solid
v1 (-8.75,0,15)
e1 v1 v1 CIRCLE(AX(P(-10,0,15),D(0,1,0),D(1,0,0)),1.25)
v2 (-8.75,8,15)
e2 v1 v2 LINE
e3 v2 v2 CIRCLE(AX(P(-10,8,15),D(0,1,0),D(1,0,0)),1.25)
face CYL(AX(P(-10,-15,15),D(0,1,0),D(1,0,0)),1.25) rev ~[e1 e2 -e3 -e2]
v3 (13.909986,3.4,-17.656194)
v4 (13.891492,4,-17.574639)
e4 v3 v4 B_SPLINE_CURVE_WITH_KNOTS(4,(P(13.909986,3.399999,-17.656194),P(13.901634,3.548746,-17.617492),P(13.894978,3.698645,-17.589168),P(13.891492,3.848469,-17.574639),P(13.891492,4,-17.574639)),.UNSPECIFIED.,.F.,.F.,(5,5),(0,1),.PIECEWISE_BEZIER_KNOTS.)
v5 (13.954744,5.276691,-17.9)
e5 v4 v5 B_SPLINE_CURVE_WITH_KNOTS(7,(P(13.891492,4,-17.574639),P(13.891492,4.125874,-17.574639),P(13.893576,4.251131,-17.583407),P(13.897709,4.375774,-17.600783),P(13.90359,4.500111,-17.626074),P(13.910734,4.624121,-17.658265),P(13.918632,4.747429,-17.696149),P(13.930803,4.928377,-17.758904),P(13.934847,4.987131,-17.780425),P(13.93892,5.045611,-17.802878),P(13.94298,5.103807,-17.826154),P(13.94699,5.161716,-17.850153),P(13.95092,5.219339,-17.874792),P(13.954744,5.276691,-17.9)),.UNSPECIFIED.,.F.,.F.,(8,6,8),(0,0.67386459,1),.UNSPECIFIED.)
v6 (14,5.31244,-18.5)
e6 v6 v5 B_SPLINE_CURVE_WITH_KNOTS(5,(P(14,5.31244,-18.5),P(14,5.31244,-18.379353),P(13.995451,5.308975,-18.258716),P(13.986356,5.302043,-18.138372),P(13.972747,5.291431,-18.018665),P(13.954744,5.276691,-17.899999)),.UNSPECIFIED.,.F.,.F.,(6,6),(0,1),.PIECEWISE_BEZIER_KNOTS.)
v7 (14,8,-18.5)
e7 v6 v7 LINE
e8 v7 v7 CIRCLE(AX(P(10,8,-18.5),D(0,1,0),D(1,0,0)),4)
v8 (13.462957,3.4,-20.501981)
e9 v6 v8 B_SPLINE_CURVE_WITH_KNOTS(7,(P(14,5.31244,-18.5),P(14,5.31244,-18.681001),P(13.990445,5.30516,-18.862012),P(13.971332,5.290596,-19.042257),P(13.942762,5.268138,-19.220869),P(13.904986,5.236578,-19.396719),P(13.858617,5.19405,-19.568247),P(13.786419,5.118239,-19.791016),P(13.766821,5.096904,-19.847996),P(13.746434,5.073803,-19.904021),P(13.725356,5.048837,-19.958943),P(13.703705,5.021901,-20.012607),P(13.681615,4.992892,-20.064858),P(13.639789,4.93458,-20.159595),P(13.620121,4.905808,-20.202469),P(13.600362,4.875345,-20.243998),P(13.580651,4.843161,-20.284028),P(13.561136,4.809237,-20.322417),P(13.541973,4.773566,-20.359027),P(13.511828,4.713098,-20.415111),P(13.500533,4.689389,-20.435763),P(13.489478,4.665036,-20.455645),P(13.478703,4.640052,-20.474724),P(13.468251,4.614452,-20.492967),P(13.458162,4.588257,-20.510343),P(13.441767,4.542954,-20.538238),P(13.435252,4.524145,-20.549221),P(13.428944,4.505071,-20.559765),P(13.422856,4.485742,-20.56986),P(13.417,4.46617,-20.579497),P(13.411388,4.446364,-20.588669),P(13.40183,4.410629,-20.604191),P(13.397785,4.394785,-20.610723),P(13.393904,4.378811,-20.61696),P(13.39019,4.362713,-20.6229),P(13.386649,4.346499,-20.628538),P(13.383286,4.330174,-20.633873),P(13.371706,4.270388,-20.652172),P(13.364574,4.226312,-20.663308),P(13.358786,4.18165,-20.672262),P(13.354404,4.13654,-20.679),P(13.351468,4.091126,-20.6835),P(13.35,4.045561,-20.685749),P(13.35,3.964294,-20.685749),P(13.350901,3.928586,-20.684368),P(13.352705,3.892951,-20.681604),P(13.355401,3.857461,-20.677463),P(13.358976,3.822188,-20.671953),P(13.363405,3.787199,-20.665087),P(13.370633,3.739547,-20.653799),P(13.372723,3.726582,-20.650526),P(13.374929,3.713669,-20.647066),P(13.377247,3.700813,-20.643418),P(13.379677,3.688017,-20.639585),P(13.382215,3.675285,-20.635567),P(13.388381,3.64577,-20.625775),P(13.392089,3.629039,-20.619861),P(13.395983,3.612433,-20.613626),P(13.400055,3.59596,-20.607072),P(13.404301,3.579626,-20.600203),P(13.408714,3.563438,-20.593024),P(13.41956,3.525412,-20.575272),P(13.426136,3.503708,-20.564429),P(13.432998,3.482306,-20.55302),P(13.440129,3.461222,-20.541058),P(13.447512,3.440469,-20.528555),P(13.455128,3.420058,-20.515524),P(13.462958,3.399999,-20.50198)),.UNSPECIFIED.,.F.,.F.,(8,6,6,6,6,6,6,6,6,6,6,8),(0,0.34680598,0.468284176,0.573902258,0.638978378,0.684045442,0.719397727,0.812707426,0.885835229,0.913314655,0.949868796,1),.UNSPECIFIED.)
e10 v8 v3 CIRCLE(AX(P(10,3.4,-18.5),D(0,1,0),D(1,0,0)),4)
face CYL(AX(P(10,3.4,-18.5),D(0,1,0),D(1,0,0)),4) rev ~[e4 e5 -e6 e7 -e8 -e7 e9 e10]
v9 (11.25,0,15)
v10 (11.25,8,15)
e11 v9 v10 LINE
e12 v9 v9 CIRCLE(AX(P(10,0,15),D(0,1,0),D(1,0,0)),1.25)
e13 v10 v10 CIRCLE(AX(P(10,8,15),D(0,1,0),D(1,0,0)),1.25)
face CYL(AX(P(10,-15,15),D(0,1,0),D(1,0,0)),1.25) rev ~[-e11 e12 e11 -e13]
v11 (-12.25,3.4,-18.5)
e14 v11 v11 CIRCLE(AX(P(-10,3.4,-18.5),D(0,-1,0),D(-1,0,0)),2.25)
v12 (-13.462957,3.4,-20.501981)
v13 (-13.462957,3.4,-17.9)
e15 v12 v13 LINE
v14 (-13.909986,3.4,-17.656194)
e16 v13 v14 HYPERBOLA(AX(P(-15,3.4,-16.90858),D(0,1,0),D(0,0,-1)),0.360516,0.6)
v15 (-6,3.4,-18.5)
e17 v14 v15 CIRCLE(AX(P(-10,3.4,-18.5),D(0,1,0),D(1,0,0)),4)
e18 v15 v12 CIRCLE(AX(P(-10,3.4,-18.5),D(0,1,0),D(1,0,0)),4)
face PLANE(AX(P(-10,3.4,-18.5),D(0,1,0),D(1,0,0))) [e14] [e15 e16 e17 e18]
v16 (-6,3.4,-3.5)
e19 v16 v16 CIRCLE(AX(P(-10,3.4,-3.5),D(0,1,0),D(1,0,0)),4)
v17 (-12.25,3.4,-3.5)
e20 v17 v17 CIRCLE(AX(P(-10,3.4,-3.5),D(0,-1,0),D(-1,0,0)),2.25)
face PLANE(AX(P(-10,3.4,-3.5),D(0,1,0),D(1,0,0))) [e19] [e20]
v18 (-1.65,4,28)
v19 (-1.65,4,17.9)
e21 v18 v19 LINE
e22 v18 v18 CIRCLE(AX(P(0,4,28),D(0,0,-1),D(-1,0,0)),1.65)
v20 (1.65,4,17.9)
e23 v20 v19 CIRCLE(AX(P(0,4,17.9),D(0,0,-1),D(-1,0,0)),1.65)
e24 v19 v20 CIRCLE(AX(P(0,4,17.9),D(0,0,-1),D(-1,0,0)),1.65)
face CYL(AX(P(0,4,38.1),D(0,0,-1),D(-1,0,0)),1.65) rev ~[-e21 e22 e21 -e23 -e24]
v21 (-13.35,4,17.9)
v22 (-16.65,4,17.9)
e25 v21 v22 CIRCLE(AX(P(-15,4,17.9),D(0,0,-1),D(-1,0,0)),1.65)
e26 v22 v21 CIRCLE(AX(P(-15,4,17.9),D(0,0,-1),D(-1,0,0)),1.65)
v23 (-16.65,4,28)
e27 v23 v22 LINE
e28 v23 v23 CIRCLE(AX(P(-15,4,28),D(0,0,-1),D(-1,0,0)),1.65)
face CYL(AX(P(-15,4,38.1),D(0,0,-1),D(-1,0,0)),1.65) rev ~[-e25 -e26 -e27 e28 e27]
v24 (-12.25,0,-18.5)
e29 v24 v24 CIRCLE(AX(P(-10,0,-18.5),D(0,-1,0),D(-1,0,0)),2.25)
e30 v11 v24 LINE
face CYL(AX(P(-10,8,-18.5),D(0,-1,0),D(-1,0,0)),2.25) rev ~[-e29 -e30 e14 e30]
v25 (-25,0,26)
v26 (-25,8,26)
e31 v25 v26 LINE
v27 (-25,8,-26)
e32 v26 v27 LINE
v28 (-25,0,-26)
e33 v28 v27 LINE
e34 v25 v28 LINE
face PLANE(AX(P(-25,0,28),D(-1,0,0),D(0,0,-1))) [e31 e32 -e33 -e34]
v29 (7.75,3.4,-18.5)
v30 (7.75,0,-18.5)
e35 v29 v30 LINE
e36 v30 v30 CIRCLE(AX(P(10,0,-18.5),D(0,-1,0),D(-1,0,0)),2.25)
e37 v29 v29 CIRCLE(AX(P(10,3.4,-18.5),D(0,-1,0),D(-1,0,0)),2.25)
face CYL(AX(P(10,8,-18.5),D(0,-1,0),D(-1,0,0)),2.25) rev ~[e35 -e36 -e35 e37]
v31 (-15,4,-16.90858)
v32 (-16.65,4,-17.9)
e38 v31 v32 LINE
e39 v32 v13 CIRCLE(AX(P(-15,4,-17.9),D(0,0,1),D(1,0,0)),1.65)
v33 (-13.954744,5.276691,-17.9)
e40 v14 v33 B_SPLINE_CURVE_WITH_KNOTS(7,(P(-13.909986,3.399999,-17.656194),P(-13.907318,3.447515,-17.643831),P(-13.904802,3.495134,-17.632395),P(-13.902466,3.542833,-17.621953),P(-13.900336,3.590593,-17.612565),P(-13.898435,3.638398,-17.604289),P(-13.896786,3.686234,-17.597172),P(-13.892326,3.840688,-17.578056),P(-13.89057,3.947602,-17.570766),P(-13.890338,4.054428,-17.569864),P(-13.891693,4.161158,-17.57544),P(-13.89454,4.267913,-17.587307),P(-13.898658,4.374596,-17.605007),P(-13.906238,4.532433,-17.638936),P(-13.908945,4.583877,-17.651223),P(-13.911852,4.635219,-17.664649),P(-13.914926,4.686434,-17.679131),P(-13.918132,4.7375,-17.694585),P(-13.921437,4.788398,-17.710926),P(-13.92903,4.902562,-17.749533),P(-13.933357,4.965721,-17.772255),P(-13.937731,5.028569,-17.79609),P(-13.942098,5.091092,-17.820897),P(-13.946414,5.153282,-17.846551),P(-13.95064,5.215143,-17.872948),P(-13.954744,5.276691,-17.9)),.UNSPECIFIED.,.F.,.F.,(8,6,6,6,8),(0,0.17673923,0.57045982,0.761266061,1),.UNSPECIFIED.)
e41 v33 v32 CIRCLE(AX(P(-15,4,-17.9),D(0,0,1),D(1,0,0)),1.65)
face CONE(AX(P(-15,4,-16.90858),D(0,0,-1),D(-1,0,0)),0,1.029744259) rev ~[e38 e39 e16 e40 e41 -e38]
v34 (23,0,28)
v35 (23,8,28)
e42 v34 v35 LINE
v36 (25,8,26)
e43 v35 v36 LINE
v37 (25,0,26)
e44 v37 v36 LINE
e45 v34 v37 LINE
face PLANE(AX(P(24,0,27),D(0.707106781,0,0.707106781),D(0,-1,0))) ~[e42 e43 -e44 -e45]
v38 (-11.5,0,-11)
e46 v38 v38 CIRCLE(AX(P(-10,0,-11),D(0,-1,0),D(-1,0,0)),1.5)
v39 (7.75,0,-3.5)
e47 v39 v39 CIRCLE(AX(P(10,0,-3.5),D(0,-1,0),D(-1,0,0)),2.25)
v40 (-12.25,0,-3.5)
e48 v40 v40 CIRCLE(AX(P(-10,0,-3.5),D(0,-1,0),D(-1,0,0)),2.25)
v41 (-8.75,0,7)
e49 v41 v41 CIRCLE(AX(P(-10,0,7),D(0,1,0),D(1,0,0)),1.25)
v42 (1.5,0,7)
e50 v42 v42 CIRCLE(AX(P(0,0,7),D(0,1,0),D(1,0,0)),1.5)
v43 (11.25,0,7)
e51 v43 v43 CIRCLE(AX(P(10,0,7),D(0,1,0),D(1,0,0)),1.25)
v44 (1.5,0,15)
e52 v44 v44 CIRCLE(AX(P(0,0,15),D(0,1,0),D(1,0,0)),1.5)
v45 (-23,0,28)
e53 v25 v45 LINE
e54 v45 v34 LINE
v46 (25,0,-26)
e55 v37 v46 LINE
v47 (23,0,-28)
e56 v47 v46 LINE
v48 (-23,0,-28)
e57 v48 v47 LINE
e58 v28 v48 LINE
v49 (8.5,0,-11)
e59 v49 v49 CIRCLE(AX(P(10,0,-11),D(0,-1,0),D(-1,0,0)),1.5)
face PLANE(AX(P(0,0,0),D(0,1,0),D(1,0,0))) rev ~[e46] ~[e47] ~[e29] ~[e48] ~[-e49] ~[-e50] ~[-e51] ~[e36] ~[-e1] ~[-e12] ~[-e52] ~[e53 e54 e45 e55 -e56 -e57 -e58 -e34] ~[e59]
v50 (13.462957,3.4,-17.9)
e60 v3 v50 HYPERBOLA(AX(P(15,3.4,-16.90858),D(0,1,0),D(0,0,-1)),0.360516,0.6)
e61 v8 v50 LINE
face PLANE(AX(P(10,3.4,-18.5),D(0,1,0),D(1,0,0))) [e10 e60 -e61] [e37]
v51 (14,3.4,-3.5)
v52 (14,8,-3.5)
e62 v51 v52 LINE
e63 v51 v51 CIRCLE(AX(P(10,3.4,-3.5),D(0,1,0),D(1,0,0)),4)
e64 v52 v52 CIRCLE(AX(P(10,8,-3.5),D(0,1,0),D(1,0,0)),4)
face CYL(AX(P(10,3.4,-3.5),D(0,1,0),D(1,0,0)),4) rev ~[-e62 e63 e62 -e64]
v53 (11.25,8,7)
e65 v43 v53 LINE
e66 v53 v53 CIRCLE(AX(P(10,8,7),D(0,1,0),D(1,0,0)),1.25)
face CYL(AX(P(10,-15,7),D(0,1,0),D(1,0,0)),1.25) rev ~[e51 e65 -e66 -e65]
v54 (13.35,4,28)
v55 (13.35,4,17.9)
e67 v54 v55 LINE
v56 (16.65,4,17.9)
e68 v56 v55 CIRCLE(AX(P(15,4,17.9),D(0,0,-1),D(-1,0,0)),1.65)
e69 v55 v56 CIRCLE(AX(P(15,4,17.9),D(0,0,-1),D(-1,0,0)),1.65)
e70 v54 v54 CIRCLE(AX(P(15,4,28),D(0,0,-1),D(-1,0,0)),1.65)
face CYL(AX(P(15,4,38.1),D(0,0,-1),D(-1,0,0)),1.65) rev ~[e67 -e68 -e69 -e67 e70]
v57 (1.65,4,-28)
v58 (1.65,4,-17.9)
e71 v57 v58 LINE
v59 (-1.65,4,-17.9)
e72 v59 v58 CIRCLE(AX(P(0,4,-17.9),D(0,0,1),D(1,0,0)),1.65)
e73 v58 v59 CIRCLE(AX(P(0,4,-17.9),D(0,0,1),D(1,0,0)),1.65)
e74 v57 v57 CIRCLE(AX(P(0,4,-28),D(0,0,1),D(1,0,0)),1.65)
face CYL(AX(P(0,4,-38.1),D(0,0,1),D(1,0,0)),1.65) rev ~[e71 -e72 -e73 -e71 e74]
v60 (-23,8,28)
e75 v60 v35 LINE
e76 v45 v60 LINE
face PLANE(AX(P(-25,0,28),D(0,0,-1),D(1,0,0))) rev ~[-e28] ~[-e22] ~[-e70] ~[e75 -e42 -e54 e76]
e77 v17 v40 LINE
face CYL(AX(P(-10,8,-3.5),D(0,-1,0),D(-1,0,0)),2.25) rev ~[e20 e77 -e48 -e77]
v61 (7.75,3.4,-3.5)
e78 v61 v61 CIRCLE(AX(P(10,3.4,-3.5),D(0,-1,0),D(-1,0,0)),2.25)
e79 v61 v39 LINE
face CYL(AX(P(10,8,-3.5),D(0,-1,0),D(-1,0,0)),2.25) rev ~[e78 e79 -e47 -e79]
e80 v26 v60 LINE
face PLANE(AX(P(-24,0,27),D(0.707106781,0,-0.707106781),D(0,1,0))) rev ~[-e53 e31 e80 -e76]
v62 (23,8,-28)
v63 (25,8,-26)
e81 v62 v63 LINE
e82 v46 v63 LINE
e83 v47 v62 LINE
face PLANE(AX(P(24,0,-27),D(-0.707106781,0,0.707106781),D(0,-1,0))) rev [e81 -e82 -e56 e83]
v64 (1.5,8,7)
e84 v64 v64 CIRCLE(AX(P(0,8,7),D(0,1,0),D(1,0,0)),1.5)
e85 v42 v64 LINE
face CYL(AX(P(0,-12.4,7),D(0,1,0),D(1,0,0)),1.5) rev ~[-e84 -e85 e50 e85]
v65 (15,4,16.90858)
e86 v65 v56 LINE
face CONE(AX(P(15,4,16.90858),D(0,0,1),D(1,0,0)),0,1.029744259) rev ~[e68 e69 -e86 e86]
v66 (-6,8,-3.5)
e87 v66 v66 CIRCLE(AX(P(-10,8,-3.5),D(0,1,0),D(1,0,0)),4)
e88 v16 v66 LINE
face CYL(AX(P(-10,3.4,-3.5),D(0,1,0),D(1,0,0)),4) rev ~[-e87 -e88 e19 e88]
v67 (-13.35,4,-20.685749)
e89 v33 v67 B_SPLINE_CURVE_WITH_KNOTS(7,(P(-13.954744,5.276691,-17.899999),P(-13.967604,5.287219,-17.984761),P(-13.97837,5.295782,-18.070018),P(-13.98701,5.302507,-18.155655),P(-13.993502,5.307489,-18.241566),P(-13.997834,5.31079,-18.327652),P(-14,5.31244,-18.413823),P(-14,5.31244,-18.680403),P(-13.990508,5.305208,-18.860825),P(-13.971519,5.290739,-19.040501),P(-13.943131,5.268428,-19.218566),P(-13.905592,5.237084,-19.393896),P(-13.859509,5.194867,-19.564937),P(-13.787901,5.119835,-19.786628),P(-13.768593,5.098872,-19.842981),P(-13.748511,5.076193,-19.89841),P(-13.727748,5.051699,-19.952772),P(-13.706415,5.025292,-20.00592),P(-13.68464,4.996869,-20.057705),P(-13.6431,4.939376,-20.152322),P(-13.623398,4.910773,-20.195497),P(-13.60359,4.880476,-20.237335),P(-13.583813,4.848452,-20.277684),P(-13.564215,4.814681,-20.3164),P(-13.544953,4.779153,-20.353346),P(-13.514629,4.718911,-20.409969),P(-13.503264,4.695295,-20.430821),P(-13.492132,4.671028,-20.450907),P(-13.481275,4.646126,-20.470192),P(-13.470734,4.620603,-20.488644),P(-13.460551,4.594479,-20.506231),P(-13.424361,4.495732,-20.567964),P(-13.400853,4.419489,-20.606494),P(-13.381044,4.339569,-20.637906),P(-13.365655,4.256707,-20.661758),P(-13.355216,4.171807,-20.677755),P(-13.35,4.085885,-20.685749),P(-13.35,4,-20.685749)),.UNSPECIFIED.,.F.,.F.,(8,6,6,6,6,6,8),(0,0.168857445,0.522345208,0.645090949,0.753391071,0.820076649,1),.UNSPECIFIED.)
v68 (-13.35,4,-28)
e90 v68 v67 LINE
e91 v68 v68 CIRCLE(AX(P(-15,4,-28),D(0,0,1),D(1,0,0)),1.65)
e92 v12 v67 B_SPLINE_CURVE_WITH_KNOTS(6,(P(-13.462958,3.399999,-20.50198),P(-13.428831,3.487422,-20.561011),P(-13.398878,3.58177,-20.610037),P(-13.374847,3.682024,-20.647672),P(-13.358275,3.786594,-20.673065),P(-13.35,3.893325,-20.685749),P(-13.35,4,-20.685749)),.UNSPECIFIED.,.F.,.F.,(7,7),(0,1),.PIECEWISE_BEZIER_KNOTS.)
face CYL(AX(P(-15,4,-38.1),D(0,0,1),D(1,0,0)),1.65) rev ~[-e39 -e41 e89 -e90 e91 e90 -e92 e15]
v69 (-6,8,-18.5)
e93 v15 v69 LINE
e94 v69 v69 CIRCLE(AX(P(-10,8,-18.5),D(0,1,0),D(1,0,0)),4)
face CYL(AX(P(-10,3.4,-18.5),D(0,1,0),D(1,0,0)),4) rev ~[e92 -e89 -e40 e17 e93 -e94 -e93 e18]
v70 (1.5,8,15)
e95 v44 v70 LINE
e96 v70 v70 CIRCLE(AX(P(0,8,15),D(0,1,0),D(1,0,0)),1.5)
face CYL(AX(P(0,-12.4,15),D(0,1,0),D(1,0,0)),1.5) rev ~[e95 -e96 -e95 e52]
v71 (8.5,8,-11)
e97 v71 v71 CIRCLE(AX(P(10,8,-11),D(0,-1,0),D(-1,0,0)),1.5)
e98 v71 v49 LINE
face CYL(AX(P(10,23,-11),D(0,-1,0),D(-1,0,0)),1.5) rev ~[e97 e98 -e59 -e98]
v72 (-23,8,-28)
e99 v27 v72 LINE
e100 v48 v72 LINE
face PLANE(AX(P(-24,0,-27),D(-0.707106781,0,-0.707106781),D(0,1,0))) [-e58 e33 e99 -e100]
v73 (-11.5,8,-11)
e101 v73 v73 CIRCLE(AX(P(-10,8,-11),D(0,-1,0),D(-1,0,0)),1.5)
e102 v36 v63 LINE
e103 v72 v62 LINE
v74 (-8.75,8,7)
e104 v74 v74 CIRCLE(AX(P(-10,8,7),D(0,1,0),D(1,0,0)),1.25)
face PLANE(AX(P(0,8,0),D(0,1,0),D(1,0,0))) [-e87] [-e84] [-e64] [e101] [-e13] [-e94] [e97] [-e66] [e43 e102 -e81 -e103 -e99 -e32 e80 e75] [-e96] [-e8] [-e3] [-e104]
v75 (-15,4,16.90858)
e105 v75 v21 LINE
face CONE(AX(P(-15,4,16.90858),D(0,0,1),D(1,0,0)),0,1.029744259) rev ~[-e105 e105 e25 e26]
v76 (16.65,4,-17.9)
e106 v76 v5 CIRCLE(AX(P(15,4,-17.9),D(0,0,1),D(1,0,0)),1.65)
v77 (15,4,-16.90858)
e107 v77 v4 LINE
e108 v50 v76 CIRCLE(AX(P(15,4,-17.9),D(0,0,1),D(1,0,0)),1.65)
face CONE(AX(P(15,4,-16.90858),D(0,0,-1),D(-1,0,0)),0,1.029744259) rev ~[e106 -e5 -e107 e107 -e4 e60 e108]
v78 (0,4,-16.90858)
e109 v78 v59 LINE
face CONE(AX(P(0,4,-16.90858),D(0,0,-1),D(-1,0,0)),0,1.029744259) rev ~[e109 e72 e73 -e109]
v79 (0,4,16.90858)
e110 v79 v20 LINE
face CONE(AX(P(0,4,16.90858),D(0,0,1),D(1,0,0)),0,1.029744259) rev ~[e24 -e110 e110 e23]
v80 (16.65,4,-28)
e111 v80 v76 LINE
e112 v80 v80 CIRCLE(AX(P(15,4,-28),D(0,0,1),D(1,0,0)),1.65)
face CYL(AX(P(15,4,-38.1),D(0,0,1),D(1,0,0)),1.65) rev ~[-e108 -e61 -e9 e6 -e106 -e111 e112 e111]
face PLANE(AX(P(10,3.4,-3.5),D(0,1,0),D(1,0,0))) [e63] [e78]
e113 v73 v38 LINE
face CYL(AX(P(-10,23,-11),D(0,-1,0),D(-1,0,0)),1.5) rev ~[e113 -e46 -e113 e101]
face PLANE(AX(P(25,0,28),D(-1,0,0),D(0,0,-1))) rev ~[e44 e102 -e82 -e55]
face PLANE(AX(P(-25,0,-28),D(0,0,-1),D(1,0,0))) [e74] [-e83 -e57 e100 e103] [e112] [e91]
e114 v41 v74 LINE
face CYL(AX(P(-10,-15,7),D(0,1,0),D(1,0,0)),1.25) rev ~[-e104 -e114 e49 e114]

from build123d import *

# Parameters (mm, degrees)
SKETCH_1_W                = 50
SKETCH_1_H                = 56
EXTRUDE_1_DEPTH           = 8
HOLE_WIZARD_M4_1_D        = 3.3
HOLE_WIZARD_M4_1_DEPTH    = 10.1
HOLE_WIZARD_M4_1_TIP      = 0.991420021
CHAMFER_1_SIZE            = 2
HOLE_WIZARD_M4_2_D        = 3.3
HOLE_WIZARD_M4_2_DEPTH    = 10.1
HOLE_WIZARD_M4_2_TIP      = 0.991420021
MM_1_D                    = 3
MM_1_DEPTH                = 12.4
MM_1_TIP                  = 0.901290929
HOLE_WIZARD_M3_1_D        = 2.5
HOLE_WIZARD_M3_1_DEPTH    = 15
HOLE_WIZARD_M3_1_TIP      = 0.751075774
MM_2_D                    = 3
MM_2_DEPTH                = 15
MM_2_TIP                  = 0.901290929
HOLE_WIZARD_1_D           = 4.5
HOLE_WIZARD_1_DEPTH       = 15
HOLE_WIZARD_1_CBORE_D     = 8
HOLE_WIZARD_1_CBORE_DEPTH = 4.6
HOLE_WIZARD_1_TIP         = 1.351936393
HOLE_WIZARD_2_D           = 4.5
HOLE_WIZARD_2_DEPTH       = 15
HOLE_WIZARD_2_CBORE_D     = 8
HOLE_WIZARD_2_CBORE_DEPTH = 4.6
HOLE_WIZARD_2_TIP         = 1.351936393
MM_3_D                    = 3
MM_3_DEPTH                = 15
MM_3_TIP                  = 0.901290929
CHAMFER_2_SIZE            = 2


with BuildPart() as part:
    # 草图1 → 凸台-拉伸1 (new body)
    with BuildSketch(Plane(origin=(0, 0, 0), x_dir=(1, 0, 0), z_dir=(0, 1, 0))):
        Rectangle(SKETCH_1_W, SKETCH_1_H)
    extrude(amount=EXTRUDE_1_DEPTH)

    # M4 螺纹孔1
    with Locations(Plane.XY.offset(28)):
        with Locations((15, 4), (0, 4), (-15, 4)):
            Hole(HOLE_WIZARD_M4_1_D / 2, depth=HOLE_WIZARD_M4_1_DEPTH)
            with Locations((0, 0, -(HOLE_WIZARD_M4_1_DEPTH + HOLE_WIZARD_M4_1_TIP / 2))):  # 118° drill point
                Cone(0, HOLE_WIZARD_M4_1_D / 2, HOLE_WIZARD_M4_1_TIP, mode=Mode.SUBTRACT)

    # 倒角1
    chamfer_1_edges = [part.edges().sort_by_distance(p)[0] for p in [
        (25, 4, 28),
        (-25, 4, 28),
    ]]
    chamfer(chamfer_1_edges, length=CHAMFER_1_SIZE)

    # M4 螺纹孔2
    with Locations(Plane(origin=(0, 0, -28), x_dir=(-1, 0, 0), z_dir=(0, 0, -1))):
        with Locations((-15, 4), (0, 4), (15, 4)):
            Hole(HOLE_WIZARD_M4_2_D / 2, depth=HOLE_WIZARD_M4_2_DEPTH)
            with Locations((0, 0, -(HOLE_WIZARD_M4_2_DEPTH + HOLE_WIZARD_M4_2_TIP / 2))):  # 118° drill point
                Cone(0, HOLE_WIZARD_M4_2_D / 2, HOLE_WIZARD_M4_2_TIP, mode=Mode.SUBTRACT)

    # 大小mm 暗销孔1
    with Locations(Plane(origin=(0, 0, 0), x_dir=(-1, 0, 0), z_dir=(0, -1, 0))):
        with Locations((0, -7), (0, -15)):
            Hole(MM_1_D / 2, depth=MM_1_DEPTH)
            with Locations((0, 0, -(MM_1_DEPTH + MM_1_TIP / 2))):  # 118° drill point
                Cone(0, MM_1_D / 2, MM_1_TIP, mode=Mode.SUBTRACT)

    # M3 螺纹孔1
    with Locations(Plane(origin=(0, 0, 0), x_dir=(-1, 0, 0), z_dir=(0, -1, 0))):
        with Locations((-10, -7), (10, -7), (-10, -15), (10, -15)):
            Hole(HOLE_WIZARD_M3_1_D / 2, depth=HOLE_WIZARD_M3_1_DEPTH)
            with Locations((0, 0, -(HOLE_WIZARD_M3_1_DEPTH + HOLE_WIZARD_M3_1_TIP / 2))):  # 118° drill point
                Cone(0, HOLE_WIZARD_M3_1_D / 2, HOLE_WIZARD_M3_1_TIP, mode=Mode.SUBTRACT)

    # 大小mm 暗销孔2
    with Locations(Plane(origin=(0, 8, 0), x_dir=(1, 0, 0), z_dir=(0, 1, 0))):
        with Locations((-10, 11)):
            Hole(MM_2_D / 2, depth=MM_2_DEPTH)
            with Locations((0, 0, -(MM_2_DEPTH + MM_2_TIP / 2))):  # 118° drill point
                Cone(0, MM_2_D / 2, MM_2_TIP, mode=Mode.SUBTRACT)

    # 打孔尺寸(%根据)内六角圆柱头螺钉的类型1
    with Locations(Plane(origin=(0, 8, 0), x_dir=(1, 0, 0), z_dir=(0, 1, 0))):
        with Locations((-10, 18.5), (-10, 3.5)):
            CounterBoreHole(HOLE_WIZARD_1_D / 2, HOLE_WIZARD_1_CBORE_D / 2, HOLE_WIZARD_1_CBORE_DEPTH, depth=HOLE_WIZARD_1_DEPTH)
            with Locations((0, 0, -(HOLE_WIZARD_1_DEPTH + HOLE_WIZARD_1_TIP / 2))):  # 118° drill point
                Cone(0, HOLE_WIZARD_1_D / 2, HOLE_WIZARD_1_TIP, mode=Mode.SUBTRACT)

    # 打孔尺寸(%根据)内六角圆柱头螺钉的类型2
    with Locations(Plane(origin=(0, 8, 0), x_dir=(1, 0, 0), z_dir=(0, 1, 0))):
        with Locations((10, 18.5), (10, 3.5)):
            CounterBoreHole(HOLE_WIZARD_2_D / 2, HOLE_WIZARD_2_CBORE_D / 2, HOLE_WIZARD_2_CBORE_DEPTH, depth=HOLE_WIZARD_2_DEPTH)
            with Locations((0, 0, -(HOLE_WIZARD_2_DEPTH + HOLE_WIZARD_2_TIP / 2))):  # 118° drill point
                Cone(0, HOLE_WIZARD_2_D / 2, HOLE_WIZARD_2_TIP, mode=Mode.SUBTRACT)

    # 大小mm 暗销孔3
    with Locations(Plane(origin=(0, 8, 0), x_dir=(1, 0, 0), z_dir=(0, 1, 0))):
        with Locations((10, 11)):
            Hole(MM_3_D / 2, depth=MM_3_DEPTH)
            with Locations((0, 0, -(MM_3_DEPTH + MM_3_TIP / 2))):  # 118° drill point
                Cone(0, MM_3_D / 2, MM_3_TIP, mode=Mode.SUBTRACT)

    # 倒角2
    chamfer_2_edges = [part.edges().sort_by_distance(p)[0] for p in [
        (-25, 4, -28),
        (25, 4, -28),
    ]]
    chamfer(chamfer_2_edges, length=CHAMFER_2_SIZE)


solid = part.part
